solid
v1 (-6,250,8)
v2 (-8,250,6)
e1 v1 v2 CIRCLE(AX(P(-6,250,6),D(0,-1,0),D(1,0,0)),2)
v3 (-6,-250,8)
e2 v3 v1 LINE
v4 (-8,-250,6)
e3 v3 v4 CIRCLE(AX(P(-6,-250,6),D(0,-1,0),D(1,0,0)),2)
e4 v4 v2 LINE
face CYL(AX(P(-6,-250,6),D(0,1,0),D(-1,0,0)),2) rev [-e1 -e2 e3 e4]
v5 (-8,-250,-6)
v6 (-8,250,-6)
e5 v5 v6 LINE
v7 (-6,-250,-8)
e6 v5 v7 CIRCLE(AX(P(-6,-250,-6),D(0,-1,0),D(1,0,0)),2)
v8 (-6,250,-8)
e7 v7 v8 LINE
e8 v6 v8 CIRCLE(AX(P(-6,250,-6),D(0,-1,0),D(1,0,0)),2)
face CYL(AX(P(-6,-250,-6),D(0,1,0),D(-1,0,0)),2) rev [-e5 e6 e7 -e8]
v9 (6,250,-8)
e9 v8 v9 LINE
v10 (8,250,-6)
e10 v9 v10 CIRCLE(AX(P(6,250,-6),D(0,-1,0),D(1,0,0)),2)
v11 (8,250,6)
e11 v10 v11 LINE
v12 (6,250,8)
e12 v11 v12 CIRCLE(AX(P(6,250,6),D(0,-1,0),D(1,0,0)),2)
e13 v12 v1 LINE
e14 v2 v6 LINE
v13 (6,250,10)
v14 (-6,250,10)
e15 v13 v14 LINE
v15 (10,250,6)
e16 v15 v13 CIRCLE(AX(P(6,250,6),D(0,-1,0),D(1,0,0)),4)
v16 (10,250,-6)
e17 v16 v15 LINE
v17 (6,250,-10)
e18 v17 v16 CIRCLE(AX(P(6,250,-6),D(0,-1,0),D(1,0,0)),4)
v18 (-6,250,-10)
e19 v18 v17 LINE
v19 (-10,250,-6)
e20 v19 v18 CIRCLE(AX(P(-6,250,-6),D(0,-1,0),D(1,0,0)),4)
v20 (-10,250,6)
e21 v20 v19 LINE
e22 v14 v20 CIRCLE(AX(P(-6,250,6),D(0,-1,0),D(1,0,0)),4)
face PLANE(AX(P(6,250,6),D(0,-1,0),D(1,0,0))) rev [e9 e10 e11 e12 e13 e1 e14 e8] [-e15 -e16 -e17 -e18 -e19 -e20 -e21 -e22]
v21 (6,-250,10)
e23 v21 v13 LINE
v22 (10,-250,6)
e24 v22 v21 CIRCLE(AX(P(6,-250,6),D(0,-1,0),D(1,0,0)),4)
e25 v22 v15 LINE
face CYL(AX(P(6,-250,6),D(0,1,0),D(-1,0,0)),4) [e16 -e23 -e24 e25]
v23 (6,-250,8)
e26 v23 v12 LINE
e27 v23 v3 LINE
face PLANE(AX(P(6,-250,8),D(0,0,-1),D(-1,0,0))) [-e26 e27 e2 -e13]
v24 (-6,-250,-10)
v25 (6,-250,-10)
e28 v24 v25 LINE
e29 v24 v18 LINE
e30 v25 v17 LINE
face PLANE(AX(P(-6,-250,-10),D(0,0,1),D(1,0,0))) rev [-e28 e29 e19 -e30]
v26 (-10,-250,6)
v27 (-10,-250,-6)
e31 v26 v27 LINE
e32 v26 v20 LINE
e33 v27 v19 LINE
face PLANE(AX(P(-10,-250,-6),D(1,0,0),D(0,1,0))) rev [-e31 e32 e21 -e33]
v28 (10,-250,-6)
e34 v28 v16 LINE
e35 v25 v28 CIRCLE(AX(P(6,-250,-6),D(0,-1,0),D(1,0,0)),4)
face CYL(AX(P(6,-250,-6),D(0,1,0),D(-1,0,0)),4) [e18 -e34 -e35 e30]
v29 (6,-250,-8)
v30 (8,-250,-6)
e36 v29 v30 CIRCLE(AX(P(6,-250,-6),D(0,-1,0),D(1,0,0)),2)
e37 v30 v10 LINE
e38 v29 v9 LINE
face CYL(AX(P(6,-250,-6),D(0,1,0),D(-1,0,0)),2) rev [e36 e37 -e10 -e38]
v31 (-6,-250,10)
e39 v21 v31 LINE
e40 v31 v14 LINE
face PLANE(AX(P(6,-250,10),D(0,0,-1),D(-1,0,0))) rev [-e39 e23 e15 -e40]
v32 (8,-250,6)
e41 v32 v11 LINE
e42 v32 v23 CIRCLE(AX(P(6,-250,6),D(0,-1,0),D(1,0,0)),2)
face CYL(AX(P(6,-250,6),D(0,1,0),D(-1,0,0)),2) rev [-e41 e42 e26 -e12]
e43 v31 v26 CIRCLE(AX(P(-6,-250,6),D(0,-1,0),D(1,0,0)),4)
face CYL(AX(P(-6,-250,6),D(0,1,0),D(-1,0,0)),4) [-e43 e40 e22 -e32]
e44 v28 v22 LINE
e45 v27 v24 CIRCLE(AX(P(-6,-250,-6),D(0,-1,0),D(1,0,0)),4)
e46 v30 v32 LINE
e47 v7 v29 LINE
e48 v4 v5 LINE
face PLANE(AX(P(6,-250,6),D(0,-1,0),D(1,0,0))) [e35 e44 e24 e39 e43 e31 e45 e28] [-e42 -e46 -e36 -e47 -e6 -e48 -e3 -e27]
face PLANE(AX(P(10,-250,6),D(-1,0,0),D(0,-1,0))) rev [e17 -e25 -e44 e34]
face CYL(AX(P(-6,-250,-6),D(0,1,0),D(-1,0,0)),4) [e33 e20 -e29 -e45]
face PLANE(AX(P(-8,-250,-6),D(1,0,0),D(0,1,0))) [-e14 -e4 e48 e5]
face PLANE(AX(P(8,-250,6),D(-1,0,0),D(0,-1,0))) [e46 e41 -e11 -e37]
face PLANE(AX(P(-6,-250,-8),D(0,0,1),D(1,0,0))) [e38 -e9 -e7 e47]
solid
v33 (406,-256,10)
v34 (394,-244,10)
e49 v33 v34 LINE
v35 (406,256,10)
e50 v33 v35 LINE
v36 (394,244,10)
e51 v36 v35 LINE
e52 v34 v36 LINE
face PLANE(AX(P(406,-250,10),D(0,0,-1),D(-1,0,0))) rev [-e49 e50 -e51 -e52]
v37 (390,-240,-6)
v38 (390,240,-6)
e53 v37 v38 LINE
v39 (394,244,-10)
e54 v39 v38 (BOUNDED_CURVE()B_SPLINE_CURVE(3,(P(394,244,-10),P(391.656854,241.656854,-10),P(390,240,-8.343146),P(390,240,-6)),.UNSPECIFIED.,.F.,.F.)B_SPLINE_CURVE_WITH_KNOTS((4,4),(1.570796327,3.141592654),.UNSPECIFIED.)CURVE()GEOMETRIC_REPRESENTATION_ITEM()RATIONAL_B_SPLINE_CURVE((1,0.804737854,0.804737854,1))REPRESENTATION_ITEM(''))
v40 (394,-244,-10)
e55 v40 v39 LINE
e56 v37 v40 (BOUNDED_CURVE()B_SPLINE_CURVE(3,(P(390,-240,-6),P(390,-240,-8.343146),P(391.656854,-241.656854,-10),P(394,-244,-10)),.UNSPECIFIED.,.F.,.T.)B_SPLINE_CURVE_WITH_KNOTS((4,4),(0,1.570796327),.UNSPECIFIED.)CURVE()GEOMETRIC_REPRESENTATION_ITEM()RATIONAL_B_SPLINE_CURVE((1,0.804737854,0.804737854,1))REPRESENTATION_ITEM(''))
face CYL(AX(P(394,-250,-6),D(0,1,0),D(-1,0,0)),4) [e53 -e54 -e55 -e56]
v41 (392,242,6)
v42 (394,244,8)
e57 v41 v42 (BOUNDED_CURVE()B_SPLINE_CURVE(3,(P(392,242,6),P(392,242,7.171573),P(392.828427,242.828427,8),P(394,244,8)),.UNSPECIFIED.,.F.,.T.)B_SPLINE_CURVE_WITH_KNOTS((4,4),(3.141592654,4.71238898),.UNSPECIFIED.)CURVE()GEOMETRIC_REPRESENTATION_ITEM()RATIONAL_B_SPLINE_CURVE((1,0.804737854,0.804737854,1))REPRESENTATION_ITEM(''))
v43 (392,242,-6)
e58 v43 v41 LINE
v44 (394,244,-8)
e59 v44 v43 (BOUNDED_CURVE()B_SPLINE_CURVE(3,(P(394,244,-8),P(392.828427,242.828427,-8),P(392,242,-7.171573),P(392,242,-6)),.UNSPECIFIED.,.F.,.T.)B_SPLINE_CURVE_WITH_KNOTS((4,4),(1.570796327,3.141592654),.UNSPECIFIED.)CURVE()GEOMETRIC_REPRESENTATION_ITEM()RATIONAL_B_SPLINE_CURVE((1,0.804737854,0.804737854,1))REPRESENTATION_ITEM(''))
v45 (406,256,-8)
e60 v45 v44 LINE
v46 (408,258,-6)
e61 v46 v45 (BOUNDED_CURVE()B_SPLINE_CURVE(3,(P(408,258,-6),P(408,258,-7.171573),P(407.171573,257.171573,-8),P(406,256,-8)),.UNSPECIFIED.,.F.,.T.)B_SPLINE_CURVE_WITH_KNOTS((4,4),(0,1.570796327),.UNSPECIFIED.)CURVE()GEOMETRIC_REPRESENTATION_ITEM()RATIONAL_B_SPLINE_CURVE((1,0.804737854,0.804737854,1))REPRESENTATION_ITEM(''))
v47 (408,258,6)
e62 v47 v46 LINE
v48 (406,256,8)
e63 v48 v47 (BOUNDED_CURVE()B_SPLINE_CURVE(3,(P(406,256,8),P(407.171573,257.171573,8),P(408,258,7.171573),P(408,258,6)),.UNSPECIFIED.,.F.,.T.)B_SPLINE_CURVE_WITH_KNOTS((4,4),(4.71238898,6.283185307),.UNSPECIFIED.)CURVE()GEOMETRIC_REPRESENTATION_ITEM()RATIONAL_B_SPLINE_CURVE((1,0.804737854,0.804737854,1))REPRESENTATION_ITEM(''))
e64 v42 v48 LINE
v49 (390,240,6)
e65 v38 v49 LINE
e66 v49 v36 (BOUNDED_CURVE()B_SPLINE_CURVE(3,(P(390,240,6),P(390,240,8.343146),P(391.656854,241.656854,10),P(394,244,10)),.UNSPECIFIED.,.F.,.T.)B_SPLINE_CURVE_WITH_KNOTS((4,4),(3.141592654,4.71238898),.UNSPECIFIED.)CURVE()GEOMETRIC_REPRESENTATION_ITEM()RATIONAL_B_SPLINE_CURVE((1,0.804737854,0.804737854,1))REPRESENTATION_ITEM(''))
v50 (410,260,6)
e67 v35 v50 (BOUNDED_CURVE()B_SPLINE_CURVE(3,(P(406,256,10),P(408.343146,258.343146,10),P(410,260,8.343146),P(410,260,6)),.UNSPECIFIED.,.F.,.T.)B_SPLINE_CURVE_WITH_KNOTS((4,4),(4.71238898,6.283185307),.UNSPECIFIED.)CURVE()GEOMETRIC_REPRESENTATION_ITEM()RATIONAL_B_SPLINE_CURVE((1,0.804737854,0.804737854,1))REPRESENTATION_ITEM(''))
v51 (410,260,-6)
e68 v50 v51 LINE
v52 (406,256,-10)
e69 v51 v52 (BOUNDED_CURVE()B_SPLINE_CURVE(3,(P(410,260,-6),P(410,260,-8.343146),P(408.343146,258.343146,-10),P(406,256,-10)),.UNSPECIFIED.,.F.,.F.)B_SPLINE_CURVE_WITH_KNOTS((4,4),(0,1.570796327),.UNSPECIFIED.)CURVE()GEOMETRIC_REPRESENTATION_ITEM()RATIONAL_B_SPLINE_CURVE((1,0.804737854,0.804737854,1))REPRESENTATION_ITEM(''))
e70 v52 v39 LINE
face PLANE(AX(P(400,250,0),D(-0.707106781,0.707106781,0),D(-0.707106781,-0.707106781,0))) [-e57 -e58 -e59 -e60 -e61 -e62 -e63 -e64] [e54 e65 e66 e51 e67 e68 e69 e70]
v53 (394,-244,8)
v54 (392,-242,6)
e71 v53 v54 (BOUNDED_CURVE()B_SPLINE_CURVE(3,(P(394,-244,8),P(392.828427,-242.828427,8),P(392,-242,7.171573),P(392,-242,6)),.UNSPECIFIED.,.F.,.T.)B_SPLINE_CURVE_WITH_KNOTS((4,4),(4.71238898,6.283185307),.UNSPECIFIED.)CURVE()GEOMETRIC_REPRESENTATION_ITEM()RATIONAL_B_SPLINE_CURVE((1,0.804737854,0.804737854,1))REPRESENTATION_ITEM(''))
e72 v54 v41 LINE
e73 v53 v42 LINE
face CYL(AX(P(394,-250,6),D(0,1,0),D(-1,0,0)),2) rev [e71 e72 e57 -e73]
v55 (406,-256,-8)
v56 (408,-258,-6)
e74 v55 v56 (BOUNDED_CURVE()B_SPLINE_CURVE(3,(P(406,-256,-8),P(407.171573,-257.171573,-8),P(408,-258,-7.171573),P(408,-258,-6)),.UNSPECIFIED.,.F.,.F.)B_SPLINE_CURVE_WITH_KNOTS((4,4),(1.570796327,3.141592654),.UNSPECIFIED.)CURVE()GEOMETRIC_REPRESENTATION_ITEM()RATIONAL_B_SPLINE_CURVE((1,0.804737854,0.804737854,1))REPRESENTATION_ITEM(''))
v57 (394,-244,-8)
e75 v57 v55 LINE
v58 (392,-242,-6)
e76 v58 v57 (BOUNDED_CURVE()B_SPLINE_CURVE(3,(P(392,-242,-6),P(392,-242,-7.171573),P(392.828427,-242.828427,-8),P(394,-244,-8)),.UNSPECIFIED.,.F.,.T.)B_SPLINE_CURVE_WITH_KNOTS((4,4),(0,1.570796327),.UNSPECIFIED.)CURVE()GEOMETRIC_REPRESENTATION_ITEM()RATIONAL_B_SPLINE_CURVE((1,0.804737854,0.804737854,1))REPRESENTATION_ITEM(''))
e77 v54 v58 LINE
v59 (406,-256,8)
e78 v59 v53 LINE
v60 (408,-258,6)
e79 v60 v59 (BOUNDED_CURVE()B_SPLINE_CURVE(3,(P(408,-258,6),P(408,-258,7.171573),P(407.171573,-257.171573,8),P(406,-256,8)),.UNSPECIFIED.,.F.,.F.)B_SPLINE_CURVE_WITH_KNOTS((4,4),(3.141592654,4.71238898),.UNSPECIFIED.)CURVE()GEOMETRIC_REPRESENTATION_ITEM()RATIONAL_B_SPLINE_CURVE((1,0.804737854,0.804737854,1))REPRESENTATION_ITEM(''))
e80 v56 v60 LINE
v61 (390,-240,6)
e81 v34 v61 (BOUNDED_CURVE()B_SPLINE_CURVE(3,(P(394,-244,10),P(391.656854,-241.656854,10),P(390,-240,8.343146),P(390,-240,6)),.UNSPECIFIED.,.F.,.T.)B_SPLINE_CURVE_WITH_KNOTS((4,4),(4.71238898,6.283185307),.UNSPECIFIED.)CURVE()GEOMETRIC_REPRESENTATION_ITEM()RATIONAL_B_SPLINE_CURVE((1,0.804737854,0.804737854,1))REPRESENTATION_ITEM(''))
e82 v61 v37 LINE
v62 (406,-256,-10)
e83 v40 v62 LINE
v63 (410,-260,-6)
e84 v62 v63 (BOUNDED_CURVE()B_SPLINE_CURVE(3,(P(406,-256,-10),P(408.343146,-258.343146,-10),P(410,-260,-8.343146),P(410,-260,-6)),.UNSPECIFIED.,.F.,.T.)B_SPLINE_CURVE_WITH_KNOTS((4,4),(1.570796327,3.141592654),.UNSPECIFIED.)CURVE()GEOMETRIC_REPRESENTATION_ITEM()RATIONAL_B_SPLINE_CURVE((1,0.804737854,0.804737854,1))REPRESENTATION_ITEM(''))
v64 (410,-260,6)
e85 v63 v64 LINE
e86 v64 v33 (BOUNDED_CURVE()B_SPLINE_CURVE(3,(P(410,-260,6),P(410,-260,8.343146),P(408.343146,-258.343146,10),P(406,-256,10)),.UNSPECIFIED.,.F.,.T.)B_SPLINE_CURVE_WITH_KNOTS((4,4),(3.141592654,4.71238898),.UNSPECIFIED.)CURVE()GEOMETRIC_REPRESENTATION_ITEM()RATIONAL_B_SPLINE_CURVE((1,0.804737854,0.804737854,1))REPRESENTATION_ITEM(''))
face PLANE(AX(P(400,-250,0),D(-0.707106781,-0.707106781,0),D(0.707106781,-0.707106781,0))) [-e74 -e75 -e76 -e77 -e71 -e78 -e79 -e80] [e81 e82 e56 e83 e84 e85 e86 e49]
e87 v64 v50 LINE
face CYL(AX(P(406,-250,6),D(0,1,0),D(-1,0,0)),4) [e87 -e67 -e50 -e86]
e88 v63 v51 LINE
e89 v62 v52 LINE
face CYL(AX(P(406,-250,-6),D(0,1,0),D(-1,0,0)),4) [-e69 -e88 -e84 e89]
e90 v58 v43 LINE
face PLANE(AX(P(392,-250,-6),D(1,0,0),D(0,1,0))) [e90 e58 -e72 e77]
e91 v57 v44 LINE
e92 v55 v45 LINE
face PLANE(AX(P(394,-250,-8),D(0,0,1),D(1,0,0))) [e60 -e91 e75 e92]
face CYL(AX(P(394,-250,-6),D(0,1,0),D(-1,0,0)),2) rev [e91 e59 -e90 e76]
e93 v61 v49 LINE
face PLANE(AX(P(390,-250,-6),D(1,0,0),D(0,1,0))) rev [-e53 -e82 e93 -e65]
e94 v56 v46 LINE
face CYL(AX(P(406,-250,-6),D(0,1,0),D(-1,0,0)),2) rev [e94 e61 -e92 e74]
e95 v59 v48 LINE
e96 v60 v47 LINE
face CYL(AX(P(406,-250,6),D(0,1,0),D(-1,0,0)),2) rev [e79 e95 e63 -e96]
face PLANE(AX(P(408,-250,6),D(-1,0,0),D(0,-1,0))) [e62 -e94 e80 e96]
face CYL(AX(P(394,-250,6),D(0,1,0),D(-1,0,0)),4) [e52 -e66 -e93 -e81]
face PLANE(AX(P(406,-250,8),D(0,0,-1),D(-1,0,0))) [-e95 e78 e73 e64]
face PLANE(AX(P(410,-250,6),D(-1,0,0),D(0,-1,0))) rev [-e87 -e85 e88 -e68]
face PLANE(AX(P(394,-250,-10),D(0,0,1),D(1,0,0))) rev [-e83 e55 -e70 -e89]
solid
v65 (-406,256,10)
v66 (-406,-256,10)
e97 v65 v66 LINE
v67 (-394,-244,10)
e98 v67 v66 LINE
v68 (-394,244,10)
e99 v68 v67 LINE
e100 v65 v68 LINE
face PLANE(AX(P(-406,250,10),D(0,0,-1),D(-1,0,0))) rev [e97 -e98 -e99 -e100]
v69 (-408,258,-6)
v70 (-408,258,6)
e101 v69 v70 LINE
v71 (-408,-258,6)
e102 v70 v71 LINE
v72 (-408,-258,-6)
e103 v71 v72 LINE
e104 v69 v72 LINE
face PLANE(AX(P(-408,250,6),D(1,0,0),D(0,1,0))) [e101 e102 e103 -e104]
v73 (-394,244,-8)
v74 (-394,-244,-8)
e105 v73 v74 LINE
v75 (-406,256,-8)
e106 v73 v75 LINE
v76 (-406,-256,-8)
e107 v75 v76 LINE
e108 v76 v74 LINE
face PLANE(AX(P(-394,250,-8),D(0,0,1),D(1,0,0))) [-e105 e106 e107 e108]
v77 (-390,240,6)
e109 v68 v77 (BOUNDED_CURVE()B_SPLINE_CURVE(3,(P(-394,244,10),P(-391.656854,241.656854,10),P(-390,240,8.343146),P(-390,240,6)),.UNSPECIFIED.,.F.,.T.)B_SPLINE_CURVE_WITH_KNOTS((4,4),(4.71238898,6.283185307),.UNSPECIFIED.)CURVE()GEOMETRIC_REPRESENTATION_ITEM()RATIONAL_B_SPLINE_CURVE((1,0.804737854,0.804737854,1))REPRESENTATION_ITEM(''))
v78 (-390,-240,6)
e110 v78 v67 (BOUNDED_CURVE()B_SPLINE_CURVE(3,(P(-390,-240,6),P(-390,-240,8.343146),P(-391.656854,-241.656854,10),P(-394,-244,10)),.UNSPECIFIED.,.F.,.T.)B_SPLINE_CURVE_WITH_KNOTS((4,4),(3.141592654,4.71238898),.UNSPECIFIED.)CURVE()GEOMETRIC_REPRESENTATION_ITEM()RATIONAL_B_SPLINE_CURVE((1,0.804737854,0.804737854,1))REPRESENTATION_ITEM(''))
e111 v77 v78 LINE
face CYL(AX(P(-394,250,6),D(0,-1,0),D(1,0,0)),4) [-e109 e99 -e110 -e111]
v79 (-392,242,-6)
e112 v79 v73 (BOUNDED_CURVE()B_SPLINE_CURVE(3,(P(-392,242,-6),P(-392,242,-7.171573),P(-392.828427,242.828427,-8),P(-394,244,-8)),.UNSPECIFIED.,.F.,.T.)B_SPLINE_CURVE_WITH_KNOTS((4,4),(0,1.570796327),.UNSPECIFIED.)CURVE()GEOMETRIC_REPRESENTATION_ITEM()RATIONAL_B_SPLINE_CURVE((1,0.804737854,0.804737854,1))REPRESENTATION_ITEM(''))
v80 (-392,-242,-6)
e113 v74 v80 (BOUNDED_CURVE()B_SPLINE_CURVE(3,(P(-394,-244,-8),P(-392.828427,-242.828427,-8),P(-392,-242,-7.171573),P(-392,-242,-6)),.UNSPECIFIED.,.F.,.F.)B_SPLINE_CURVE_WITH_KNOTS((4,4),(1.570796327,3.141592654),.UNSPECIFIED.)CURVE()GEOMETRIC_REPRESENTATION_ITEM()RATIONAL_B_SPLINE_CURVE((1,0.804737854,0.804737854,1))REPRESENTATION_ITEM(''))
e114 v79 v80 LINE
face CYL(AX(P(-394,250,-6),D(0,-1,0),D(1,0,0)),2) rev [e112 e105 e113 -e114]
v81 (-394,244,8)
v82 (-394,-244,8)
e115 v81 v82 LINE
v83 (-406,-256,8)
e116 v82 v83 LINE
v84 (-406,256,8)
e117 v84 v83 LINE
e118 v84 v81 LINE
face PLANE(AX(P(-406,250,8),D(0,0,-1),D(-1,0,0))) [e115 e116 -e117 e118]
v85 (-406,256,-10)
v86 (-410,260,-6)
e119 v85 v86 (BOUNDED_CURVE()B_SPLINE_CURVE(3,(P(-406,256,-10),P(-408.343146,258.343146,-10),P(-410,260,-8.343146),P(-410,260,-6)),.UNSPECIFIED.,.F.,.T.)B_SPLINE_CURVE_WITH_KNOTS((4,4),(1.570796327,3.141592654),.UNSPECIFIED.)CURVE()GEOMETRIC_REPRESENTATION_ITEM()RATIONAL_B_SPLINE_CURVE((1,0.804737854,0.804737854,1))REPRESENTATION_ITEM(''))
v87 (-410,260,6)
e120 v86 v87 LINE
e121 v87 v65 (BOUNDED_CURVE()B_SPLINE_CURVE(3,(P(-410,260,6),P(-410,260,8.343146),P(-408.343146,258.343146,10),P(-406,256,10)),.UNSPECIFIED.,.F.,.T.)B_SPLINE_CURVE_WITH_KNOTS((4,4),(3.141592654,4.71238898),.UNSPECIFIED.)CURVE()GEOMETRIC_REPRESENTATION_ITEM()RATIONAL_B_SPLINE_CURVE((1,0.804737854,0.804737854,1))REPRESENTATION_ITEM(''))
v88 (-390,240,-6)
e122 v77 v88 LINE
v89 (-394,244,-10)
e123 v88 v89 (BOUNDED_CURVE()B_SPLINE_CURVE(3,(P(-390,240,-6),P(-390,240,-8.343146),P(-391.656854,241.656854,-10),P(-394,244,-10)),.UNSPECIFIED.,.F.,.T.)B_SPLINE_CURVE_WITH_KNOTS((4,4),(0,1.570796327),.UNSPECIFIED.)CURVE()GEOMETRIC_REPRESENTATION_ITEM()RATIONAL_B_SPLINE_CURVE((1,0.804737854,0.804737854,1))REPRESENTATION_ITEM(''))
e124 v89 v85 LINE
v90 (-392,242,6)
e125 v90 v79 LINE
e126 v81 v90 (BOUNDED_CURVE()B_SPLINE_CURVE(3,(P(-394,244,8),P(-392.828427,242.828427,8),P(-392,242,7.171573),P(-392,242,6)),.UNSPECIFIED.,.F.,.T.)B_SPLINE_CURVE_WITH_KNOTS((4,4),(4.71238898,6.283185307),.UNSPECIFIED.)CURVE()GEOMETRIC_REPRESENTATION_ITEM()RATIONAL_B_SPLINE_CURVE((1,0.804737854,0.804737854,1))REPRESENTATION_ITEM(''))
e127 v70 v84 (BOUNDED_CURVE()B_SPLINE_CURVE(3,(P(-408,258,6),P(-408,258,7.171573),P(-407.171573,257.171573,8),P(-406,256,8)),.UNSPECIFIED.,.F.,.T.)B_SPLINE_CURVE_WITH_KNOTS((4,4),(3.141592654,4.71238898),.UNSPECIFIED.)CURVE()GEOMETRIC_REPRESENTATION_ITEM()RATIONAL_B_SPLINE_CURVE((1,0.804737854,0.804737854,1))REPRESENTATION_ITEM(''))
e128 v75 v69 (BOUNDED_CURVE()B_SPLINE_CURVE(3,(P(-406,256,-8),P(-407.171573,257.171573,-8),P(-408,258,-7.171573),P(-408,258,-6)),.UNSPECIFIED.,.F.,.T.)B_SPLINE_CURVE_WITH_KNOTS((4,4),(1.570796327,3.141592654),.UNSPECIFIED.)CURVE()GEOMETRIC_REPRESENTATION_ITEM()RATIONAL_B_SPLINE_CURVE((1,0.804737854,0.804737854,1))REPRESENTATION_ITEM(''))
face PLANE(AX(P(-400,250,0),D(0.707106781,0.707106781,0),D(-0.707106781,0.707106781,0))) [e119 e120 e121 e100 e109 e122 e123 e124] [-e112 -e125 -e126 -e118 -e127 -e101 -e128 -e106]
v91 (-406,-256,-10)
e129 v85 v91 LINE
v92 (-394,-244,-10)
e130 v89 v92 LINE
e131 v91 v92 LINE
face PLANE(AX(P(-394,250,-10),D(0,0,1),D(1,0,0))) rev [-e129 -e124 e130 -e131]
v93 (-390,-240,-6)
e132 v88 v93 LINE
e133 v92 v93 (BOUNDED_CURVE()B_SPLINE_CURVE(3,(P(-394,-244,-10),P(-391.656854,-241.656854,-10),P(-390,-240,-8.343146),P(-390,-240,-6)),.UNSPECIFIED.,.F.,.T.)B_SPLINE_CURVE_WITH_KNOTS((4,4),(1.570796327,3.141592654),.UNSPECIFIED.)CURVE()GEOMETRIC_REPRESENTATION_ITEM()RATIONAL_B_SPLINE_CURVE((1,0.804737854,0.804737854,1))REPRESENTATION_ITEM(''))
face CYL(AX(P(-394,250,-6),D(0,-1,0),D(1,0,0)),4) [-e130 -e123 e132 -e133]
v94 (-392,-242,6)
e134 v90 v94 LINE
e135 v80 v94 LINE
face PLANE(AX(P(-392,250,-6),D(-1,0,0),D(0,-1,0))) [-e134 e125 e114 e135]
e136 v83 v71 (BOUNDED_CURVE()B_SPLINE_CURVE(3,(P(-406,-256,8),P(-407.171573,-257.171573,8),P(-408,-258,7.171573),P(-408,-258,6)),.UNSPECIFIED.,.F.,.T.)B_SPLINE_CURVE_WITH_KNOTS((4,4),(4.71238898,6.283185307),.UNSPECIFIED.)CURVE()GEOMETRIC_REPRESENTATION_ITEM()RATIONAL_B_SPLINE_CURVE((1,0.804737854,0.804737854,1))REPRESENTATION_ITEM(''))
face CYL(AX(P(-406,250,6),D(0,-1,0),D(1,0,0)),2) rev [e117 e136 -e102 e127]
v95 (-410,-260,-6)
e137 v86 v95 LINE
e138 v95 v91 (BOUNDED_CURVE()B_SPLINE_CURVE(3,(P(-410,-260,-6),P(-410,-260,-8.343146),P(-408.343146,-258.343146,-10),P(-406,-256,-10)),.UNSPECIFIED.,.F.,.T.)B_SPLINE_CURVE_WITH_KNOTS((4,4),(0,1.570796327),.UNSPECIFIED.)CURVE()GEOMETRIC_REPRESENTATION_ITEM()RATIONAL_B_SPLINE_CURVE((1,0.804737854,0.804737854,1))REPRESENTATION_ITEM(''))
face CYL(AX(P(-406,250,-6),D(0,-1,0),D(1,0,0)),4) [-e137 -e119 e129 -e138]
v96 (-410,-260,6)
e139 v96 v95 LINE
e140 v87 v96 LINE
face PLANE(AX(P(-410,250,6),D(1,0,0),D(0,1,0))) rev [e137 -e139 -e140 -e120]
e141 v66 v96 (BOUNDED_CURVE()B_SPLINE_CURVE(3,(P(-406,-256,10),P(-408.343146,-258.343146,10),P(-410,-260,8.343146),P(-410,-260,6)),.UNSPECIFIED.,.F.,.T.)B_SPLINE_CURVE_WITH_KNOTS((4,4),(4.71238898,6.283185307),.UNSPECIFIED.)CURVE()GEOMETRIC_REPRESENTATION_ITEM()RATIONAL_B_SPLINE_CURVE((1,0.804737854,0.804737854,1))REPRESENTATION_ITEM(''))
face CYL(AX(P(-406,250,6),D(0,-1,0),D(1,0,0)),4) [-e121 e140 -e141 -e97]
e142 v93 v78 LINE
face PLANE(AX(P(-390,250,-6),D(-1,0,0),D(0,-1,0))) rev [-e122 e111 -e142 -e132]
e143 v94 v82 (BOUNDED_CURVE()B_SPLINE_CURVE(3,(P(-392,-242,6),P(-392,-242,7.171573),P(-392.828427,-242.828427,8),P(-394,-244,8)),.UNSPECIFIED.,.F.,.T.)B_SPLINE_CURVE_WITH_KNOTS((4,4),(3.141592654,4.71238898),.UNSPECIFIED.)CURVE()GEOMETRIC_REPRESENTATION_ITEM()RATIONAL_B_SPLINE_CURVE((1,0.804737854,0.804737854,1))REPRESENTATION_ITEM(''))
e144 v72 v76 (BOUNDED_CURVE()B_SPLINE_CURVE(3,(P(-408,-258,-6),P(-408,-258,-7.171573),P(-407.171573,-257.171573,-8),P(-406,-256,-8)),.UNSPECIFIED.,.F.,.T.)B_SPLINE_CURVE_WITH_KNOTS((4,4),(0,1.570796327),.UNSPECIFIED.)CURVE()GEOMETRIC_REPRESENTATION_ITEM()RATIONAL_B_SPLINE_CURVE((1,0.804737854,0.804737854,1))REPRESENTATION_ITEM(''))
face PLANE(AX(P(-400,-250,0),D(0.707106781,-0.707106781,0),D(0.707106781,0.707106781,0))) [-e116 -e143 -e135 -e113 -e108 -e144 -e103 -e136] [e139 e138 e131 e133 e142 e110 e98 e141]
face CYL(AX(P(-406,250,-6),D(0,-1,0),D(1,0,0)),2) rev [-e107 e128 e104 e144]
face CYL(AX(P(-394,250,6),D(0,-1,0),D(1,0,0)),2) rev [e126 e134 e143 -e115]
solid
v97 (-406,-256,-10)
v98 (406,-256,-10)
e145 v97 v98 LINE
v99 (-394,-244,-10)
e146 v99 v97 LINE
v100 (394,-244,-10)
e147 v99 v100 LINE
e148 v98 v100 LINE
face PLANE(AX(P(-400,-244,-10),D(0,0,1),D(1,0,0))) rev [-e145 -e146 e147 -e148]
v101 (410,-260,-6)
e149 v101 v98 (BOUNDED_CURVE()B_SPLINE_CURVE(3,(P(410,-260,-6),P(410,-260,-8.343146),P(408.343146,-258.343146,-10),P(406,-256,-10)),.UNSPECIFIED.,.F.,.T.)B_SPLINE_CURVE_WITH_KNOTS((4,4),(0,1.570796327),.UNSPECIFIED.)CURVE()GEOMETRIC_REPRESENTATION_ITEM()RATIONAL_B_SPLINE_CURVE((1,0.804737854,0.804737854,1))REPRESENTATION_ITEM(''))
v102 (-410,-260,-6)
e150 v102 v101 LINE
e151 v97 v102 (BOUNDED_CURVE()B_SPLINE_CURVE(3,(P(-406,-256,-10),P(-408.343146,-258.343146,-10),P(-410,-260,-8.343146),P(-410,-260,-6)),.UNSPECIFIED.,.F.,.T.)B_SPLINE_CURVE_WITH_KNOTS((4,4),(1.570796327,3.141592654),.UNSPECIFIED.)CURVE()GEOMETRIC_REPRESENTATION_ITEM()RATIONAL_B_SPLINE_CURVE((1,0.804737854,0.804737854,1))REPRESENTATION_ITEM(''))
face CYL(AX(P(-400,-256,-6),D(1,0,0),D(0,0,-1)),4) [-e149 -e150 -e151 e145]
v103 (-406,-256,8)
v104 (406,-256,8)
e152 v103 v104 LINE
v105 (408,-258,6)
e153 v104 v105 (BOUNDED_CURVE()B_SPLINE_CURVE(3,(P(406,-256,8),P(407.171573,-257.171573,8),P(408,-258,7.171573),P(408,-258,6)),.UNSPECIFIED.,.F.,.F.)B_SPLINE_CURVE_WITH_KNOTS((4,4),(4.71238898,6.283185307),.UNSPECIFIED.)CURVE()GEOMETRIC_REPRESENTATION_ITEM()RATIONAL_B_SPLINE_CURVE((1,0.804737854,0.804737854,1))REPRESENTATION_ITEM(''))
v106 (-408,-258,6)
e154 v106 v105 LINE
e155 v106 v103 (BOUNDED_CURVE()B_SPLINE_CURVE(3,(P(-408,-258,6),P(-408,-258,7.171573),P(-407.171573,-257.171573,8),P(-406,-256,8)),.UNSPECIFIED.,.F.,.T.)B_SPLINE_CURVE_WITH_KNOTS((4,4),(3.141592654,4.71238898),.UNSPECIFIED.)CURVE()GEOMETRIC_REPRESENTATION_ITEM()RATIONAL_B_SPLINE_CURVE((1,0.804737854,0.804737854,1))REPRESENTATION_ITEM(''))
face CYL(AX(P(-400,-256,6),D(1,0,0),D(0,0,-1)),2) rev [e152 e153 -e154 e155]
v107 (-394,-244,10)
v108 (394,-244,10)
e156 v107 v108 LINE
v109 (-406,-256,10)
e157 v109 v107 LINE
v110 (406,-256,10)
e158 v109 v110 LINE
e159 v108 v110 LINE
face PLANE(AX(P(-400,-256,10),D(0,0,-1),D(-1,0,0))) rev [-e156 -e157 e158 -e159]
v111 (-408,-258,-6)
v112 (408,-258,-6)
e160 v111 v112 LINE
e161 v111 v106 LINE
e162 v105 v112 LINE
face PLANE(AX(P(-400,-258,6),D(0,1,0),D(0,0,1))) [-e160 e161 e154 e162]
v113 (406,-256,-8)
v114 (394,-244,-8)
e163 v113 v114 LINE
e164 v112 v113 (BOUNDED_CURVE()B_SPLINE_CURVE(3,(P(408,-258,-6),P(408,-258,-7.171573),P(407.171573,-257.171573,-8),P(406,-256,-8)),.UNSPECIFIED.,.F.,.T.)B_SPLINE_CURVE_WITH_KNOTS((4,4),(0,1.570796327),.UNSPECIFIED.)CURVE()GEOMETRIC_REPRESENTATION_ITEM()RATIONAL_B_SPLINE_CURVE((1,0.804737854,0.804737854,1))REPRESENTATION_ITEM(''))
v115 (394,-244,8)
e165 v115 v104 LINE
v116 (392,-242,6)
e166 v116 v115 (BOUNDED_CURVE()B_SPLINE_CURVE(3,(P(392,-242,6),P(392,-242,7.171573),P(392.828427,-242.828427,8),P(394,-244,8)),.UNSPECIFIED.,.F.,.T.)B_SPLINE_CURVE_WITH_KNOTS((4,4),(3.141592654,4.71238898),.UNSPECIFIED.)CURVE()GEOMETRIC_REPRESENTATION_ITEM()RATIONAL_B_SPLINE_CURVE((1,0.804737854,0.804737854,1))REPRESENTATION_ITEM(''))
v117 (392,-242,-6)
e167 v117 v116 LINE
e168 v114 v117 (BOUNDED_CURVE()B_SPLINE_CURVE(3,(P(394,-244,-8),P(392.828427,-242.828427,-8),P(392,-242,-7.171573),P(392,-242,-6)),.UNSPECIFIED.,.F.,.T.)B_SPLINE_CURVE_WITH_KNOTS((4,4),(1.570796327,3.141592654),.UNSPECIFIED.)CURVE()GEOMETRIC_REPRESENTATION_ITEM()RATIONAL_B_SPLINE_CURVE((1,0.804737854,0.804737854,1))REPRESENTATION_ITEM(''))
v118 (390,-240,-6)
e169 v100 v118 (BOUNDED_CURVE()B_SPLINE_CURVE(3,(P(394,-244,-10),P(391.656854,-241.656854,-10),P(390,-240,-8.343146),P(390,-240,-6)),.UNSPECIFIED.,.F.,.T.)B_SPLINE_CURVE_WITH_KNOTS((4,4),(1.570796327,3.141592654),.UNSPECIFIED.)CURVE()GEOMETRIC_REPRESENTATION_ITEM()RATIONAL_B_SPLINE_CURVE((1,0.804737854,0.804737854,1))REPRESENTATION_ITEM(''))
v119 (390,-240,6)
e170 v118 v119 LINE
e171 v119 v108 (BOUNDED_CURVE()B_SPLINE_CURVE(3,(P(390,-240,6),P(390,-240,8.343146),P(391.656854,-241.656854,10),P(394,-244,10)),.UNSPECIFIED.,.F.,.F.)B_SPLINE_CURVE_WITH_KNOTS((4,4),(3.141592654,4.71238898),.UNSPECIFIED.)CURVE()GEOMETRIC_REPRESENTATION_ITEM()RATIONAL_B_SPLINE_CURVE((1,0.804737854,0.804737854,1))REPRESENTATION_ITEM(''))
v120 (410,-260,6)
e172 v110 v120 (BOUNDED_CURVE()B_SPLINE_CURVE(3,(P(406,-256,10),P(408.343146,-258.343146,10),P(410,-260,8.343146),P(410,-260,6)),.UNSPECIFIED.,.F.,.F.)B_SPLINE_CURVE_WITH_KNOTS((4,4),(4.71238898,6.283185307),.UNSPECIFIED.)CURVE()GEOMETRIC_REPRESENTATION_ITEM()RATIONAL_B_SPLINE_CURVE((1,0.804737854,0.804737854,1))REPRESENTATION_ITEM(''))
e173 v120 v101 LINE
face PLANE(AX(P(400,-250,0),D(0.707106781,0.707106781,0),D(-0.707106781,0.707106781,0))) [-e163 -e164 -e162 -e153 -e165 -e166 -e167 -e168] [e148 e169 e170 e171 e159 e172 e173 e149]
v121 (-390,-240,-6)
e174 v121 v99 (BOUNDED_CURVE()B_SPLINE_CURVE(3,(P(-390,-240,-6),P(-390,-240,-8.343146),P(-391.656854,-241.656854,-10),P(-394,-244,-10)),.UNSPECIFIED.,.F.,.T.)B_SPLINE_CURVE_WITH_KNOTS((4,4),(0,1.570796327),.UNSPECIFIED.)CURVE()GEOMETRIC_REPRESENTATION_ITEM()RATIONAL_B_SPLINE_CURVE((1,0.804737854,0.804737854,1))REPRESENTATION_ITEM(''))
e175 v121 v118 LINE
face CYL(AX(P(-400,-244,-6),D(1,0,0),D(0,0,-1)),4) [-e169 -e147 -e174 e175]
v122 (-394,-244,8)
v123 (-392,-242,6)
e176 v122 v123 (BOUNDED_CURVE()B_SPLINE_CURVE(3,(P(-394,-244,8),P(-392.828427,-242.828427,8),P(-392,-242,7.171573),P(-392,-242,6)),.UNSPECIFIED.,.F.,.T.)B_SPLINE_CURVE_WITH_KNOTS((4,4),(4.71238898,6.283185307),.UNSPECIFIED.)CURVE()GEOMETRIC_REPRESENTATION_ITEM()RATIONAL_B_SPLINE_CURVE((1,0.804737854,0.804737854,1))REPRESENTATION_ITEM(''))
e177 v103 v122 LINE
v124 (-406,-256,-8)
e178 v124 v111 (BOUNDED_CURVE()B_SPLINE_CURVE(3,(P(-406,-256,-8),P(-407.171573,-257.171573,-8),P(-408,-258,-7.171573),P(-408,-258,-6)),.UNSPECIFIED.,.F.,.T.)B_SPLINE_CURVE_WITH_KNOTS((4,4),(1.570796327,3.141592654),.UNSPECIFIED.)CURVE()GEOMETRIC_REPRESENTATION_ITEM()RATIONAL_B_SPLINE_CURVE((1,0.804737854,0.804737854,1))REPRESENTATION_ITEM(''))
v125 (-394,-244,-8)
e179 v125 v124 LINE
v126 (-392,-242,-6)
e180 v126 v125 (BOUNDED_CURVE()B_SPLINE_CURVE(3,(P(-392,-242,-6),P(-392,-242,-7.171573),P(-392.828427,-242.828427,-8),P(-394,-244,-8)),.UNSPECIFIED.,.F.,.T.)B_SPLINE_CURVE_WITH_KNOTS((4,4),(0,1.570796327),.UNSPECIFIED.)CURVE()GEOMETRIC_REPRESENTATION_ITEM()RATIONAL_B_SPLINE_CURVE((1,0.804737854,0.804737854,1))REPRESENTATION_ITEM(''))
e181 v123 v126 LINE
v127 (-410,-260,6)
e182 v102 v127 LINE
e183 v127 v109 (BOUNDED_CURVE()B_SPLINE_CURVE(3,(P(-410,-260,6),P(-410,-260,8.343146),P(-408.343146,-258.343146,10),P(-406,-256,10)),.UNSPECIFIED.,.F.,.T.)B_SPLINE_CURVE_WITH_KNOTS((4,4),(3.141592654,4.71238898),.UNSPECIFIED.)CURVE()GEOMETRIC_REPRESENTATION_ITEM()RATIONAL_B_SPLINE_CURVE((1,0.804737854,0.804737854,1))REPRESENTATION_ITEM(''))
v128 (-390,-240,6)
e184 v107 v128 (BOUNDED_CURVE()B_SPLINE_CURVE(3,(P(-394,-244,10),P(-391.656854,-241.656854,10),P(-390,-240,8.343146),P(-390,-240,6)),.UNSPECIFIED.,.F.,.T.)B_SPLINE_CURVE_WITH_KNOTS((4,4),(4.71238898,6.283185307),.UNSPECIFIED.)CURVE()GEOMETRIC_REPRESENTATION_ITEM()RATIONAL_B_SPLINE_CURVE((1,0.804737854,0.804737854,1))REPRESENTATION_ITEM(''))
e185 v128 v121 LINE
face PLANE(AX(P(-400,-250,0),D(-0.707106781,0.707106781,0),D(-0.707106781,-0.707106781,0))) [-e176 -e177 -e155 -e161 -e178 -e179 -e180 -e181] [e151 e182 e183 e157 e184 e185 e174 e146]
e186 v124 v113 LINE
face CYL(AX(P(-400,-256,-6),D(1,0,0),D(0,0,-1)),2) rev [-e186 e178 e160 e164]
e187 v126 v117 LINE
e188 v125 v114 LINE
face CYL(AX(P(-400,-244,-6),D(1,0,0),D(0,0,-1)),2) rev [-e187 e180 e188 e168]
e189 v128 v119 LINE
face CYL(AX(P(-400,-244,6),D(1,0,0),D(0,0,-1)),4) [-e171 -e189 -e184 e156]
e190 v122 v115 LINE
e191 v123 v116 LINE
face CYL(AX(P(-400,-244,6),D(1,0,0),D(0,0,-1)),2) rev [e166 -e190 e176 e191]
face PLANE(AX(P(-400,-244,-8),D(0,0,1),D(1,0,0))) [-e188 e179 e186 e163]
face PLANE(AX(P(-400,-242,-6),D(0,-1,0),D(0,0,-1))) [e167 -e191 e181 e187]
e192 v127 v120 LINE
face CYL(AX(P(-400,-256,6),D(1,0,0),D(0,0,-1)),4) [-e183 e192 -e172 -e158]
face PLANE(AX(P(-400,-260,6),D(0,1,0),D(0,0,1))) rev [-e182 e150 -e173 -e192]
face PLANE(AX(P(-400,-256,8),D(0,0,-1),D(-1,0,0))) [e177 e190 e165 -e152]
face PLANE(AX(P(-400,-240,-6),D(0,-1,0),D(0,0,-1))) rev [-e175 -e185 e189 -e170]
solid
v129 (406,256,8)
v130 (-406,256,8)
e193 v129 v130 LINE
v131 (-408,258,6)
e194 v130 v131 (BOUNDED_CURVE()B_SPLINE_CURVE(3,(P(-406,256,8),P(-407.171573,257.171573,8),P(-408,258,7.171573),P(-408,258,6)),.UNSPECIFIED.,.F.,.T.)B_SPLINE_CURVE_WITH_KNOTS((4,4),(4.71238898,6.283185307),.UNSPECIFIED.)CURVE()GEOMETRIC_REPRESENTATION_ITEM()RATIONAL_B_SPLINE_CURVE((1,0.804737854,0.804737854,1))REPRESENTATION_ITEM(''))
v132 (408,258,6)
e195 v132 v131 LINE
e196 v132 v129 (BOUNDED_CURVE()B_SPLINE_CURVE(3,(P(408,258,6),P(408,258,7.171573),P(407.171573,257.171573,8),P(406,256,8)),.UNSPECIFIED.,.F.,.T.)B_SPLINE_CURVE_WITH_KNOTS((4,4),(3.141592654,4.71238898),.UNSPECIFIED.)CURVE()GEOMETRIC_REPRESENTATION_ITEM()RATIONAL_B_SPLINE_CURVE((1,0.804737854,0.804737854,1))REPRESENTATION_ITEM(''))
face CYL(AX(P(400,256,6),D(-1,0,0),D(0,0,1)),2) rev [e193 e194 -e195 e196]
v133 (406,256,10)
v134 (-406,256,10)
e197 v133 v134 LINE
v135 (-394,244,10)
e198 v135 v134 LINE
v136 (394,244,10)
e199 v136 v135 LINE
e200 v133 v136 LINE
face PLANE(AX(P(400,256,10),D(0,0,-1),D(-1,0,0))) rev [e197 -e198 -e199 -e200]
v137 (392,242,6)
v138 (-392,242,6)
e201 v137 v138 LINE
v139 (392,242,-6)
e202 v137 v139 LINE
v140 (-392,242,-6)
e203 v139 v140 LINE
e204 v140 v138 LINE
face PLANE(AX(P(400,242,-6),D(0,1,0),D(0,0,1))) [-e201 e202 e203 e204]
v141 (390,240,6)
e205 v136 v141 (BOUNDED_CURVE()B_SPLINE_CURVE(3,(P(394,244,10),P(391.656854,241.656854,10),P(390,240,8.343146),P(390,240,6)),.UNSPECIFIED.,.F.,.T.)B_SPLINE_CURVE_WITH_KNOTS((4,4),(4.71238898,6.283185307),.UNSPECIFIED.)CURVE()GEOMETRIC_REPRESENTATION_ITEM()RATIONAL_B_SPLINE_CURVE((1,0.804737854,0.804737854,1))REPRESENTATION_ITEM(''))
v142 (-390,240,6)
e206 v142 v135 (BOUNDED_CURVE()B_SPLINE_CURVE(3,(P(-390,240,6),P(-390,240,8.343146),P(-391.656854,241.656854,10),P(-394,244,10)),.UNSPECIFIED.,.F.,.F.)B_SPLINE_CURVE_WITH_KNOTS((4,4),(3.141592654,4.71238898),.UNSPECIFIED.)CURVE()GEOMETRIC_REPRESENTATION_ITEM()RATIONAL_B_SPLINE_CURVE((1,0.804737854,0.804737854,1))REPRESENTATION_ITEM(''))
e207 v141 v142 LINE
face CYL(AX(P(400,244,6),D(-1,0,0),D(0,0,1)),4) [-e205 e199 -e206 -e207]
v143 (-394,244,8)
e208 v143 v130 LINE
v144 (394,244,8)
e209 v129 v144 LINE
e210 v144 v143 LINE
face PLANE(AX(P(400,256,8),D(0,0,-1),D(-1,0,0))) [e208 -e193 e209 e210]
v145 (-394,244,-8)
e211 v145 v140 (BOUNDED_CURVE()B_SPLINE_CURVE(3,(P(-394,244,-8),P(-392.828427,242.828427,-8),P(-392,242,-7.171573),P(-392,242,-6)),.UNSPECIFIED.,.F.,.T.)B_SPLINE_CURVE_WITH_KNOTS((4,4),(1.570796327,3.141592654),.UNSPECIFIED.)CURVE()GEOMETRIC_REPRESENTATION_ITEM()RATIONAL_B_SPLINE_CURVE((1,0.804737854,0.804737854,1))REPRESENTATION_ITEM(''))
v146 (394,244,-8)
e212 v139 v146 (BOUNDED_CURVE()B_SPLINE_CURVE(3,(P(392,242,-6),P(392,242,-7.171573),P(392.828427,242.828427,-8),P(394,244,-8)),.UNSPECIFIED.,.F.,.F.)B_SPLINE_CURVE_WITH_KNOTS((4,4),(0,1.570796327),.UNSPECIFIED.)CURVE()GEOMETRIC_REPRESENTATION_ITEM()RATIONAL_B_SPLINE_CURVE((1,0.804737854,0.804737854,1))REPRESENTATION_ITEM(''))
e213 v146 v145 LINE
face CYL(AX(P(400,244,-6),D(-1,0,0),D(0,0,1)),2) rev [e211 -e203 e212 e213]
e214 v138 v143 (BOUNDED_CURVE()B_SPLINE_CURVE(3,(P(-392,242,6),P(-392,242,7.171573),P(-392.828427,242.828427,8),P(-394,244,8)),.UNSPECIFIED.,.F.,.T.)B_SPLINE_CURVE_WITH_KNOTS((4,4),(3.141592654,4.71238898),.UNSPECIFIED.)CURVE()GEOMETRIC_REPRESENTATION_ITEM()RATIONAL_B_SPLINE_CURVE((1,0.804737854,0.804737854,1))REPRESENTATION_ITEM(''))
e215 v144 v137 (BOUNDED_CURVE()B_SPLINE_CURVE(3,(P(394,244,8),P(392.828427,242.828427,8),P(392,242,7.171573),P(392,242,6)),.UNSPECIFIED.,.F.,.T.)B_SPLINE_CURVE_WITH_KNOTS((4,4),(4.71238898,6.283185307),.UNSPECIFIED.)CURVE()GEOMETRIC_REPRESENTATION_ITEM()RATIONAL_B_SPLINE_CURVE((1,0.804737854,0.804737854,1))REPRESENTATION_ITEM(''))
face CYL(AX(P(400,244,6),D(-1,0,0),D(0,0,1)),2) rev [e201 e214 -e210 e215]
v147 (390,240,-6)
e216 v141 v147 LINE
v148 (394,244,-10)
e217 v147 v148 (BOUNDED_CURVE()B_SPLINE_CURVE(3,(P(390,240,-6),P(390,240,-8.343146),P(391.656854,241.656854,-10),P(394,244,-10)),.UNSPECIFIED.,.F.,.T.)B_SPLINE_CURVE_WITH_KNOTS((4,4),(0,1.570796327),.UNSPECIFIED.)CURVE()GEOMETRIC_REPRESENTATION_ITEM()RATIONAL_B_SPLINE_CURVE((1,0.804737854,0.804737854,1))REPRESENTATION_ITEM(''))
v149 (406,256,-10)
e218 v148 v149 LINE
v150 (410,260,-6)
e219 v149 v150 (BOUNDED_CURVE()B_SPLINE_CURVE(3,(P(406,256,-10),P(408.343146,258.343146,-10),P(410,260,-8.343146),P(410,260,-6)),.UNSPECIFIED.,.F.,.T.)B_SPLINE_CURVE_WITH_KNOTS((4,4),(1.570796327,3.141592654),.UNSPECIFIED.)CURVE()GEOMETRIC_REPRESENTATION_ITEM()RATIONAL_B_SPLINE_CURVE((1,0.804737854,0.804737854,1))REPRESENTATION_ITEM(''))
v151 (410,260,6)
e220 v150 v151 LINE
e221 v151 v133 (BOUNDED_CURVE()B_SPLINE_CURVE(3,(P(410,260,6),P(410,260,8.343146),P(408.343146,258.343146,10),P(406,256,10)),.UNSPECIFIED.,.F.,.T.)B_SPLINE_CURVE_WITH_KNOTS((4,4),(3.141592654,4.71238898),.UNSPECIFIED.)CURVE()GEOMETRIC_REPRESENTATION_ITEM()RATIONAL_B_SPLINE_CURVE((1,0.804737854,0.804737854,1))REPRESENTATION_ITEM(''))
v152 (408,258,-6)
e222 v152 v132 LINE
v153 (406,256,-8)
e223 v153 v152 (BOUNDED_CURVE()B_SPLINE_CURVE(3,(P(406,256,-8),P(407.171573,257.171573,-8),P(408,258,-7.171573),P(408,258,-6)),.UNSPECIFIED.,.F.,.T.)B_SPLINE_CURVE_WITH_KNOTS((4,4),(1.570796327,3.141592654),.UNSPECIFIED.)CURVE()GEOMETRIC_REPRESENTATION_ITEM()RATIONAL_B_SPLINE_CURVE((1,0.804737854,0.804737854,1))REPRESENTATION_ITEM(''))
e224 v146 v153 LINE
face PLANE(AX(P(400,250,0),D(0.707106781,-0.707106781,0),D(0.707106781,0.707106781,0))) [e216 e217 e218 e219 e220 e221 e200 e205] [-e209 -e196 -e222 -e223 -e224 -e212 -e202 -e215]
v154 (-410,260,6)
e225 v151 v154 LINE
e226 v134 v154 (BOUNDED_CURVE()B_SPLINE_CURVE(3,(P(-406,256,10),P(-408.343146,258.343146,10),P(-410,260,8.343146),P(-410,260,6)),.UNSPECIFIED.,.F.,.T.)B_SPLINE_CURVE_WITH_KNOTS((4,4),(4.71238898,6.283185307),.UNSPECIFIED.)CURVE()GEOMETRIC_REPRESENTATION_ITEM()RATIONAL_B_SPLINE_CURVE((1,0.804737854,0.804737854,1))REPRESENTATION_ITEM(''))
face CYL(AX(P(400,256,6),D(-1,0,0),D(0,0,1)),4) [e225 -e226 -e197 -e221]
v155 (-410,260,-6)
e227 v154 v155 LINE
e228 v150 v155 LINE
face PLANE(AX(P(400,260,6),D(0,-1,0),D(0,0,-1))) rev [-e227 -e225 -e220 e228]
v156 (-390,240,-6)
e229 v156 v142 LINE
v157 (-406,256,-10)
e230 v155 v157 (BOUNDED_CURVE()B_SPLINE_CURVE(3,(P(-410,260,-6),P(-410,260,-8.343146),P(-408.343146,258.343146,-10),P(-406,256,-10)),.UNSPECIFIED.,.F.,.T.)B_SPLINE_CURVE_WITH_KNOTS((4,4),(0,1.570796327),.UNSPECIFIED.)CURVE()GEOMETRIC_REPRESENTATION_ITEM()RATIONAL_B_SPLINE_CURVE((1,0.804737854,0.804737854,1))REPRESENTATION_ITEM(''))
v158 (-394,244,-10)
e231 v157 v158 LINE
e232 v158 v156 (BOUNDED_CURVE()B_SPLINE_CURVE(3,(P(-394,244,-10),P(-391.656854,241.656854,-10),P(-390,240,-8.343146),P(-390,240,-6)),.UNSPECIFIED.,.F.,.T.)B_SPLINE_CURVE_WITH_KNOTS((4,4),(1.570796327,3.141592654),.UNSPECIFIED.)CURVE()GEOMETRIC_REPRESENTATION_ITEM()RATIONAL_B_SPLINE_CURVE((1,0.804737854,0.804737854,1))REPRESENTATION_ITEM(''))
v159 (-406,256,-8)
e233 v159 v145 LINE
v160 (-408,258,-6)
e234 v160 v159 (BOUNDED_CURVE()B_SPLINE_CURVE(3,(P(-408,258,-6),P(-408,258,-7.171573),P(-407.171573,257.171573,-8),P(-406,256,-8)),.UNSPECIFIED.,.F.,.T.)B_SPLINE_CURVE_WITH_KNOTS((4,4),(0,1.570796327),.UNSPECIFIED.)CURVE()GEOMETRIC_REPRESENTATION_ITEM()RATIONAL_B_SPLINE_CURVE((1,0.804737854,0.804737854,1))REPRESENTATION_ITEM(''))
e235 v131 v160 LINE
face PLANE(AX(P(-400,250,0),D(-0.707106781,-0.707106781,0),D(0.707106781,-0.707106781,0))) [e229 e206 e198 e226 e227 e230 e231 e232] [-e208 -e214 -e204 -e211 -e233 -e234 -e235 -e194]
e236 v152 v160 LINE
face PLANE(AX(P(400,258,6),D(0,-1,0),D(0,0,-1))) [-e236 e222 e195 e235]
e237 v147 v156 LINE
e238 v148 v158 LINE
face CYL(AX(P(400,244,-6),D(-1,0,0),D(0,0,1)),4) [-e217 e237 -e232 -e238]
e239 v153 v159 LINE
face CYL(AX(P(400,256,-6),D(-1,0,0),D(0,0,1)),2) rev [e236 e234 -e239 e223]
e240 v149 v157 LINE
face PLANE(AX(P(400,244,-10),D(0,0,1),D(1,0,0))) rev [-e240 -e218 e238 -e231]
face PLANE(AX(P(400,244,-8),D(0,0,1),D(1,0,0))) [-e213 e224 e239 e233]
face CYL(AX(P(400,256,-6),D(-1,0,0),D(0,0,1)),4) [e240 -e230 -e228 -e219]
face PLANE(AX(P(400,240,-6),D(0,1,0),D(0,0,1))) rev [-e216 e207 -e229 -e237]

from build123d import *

# Parameters (mm, degrees)
SQUARE_TUBE_20_X_20_X_2_1_DEPTH      = 815.142135624
SQUARE_TUBE_20_X_20_X_2_1_DEPTH_BACK = 15.142135624
SQUARE_TUBE_20_X_20_X_2_1_2_DEPTH    = 530.284271247
SQUARE_TUBE_20_X_20_X_2_1_3_DEPTH    = 830.284271247
SQUARE_TUBE_20_X_20_X_2_1_4_DEPTH    = 530.284271247
SQUARE_TUBE_20_X_20_X_2_2_DEPTH      = 500


with BuildPart() as part:
    # Sketch1 → Square tube 20 X 20 X 2(1) (new, two sides: drawn at the far end of the back side and taken through both)
    with BuildSketch(Plane(origin=(-400, 250, 0), x_dir=(0, 1, 0), z_dir=(1, 0, 0)).offset(-SQUARE_TUBE_20_X_20_X_2_1_DEPTH_BACK)):
        with BuildLine():
            Line((-6, -10), (6, -10))
            ThreePointArc((6, -10), (8.828427125, -8.828427125), (10, -6))
            Line((10, -6), (10, 6))
            ThreePointArc((10, 6), (8.828427125, 8.828427125), (6, 10))
            Line((6, 10), (-6, 10))
            ThreePointArc((-6, 10), (-8.828427125, 8.828427125), (-10, 6))
            Line((-10, 6), (-10, -6))
            ThreePointArc((-10, -6), (-8.828427125, -8.828427125), (-6, -10))
        make_face()
        with BuildLine():
            Line((-6, -8), (6, -8))
            ThreePointArc((6, -8), (7.414213562, -7.414213562), (8, -6))
            Line((8, -6), (8, 6))
            ThreePointArc((8, 6), (7.414213562, 7.414213562), (6, 8))
            Line((6, 8), (-6, 8))
            ThreePointArc((-6, 8), (-7.414213562, 7.414213562), (-8, 6))
            Line((-8, 6), (-8, -6))
            ThreePointArc((-8, -6), (-7.414213562, -7.414213562), (-6, -8))
        make_face(mode=Mode.SUBTRACT)
    extrude(amount=SQUARE_TUBE_20_X_20_X_2_1_DEPTH + SQUARE_TUBE_20_X_20_X_2_1_DEPTH_BACK)

    # Square tube 20 X 20 X 2(1) mitre 1
    split(bisect_by=Plane(origin=(-400, 250, 0), x_dir=(-0.707106781, 0.707106781, 0), z_dir=(0.707106781, 0.707106781, 0)), keep=Keep.TOP)

    # Square tube 20 X 20 X 2(1) mitre 2
    split(bisect_by=Plane(origin=(400, 250, 0), x_dir=(-0.707106781, -0.707106781, 0), z_dir=(-0.707106781, 0.707106781, 0)), keep=Keep.TOP)


with BuildPart() as body_2:
    # Sketch1 on segment 2 (carried to segment 2) → Square tube 20 X 20 X 2_1 2 (new body)
    with BuildSketch(Plane(origin=(400, 265.142135624, 0), x_dir=(1, 0, 0), z_dir=(0, -1, 0))):
        with BuildLine():
            Line((-6, -10), (6, -10))
            ThreePointArc((6, -10), (8.828427125, -8.828427125), (10, -6))
            Line((10, -6), (10, 6))
            ThreePointArc((10, 6), (8.828427125, 8.828427125), (6, 10))
            Line((6, 10), (-6, 10))
            ThreePointArc((-6, 10), (-8.828427125, 8.828427125), (-10, 6))
            Line((-10, 6), (-10, -6))
            ThreePointArc((-10, -6), (-8.828427125, -8.828427125), (-6, -10))
        make_face()
        with BuildLine():
            Line((-6, -8), (6, -8))
            ThreePointArc((6, -8), (7.414213562, -7.414213562), (8, -6))
            Line((8, -6), (8, 6))
            ThreePointArc((8, 6), (7.414213562, 7.414213562), (6, 8))
            Line((6, 8), (-6, 8))
            ThreePointArc((-6, 8), (-7.414213562, 7.414213562), (-8, 6))
            Line((-8, 6), (-8, -6))
            ThreePointArc((-8, -6), (-7.414213562, -7.414213562), (-6, -8))
        make_face(mode=Mode.SUBTRACT)
    extrude(amount=SQUARE_TUBE_20_X_20_X_2_1_2_DEPTH)

    # Square tube 20 X 20 X 2_1 2 mitre 1
    split(bisect_by=Plane(origin=(400, 250, 0), x_dir=(0.707106781, 0.707106781, 0), z_dir=(0.707106781, -0.707106781, 0)), keep=Keep.TOP)

    # Square tube 20 X 20 X 2_1 2 mitre 2
    split(bisect_by=Plane(origin=(400, -250, 0), x_dir=(-0.707106781, 0.707106781, 0), z_dir=(0.707106781, 0.707106781, 0)), keep=Keep.TOP)


with BuildPart() as body_3:
    # Sketch1 on segment 3 (carried to segment 3) → Square tube 20 X 20 X 2_1 3 (new body)
    with BuildSketch(Plane(origin=(415.142135624, -250, 0), x_dir=(0, -1, 0), z_dir=(-1, 0, 0))):
        with BuildLine():
            Line((-6, -10), (6, -10))
            ThreePointArc((6, -10), (8.828427125, -8.828427125), (10, -6))
            Line((10, -6), (10, 6))
            ThreePointArc((10, 6), (8.828427125, 8.828427125), (6, 10))
            Line((6, 10), (-6, 10))
            ThreePointArc((-6, 10), (-8.828427125, 8.828427125), (-10, 6))
            Line((-10, 6), (-10, -6))
            ThreePointArc((-10, -6), (-8.828427125, -8.828427125), (-6, -10))
        make_face()
        with BuildLine():
            Line((-6, -8), (6, -8))
            ThreePointArc((6, -8), (7.414213562, -7.414213562), (8, -6))
            Line((8, -6), (8, 6))
            ThreePointArc((8, 6), (7.414213562, 7.414213562), (6, 8))
            Line((6, 8), (-6, 8))
            ThreePointArc((-6, 8), (-7.414213562, 7.414213562), (-8, 6))
            Line((-8, 6), (-8, -6))
            ThreePointArc((-8, -6), (-7.414213562, -7.414213562), (-6, -8))
        make_face(mode=Mode.SUBTRACT)
    extrude(amount=SQUARE_TUBE_20_X_20_X_2_1_3_DEPTH)

    # Square tube 20 X 20 X 2_1 3 mitre 1
    split(bisect_by=Plane(origin=(-400, -250, 0), x_dir=(0.707106781, 0.707106781, 0), z_dir=(0.707106781, -0.707106781, 0)), keep=Keep.TOP)

    # Square tube 20 X 20 X 2_1 3 mitre 2
    split(bisect_by=Plane(origin=(400, -250, 0), x_dir=(0.707106781, -0.707106781, 0), z_dir=(-0.707106781, -0.707106781, 0)), keep=Keep.TOP)


with BuildPart() as body_4:
    # Sketch1 on segment 4 (carried to segment 4) → Square tube 20 X 20 X 2_1 4 (new body)
    with BuildSketch(Plane(origin=(-400, -265.142135624, 0), x_dir=(-1, 0, 0), z_dir=(0, 1, 0))):
        with BuildLine():
            Line((-6, -10), (6, -10))
            ThreePointArc((6, -10), (8.828427125, -8.828427125), (10, -6))
            Line((10, -6), (10, 6))
            ThreePointArc((10, 6), (8.828427125, 8.828427125), (6, 10))
            Line((6, 10), (-6, 10))
            ThreePointArc((-6, 10), (-8.828427125, 8.828427125), (-10, 6))
            Line((-10, 6), (-10, -6))
            ThreePointArc((-10, -6), (-8.828427125, -8.828427125), (-6, -10))
        make_face()
        with BuildLine():
            Line((-6, -8), (6, -8))
            ThreePointArc((6, -8), (7.414213562, -7.414213562), (8, -6))
            Line((8, -6), (8, 6))
            ThreePointArc((8, 6), (7.414213562, 7.414213562), (6, 8))
            Line((6, 8), (-6, 8))
            ThreePointArc((-6, 8), (-7.414213562, 7.414213562), (-8, 6))
            Line((-8, 6), (-8, -6))
            ThreePointArc((-8, -6), (-7.414213562, -7.414213562), (-6, -8))
        make_face(mode=Mode.SUBTRACT)
    extrude(amount=SQUARE_TUBE_20_X_20_X_2_1_4_DEPTH)

    # Square tube 20 X 20 X 2_1 4 mitre 1
    split(bisect_by=Plane(origin=(-400, 250, 0), x_dir=(0.707106781, -0.707106781, 0), z_dir=(-0.707106781, -0.707106781, 0)), keep=Keep.TOP)

    # Square tube 20 X 20 X 2_1 4 mitre 2
    split(bisect_by=Plane(origin=(-400, -250, 0), x_dir=(-0.707106781, -0.707106781, 0), z_dir=(-0.707106781, 0.707106781, 0)), keep=Keep.TOP)


with BuildPart() as body_5:
    # Sketch11 → Square tube 20 X 20 X 2(2) (new body)
    with BuildSketch(Plane.XZ.offset(-250)):
        with BuildLine():
            Line((-6, -10), (6, -10))
            ThreePointArc((6, -10), (8.828427125, -8.828427125), (10, -6))
            Line((10, -6), (10, 6))
            ThreePointArc((10, 6), (8.828427125, 8.828427125), (6, 10))
            Line((6, 10), (-6, 10))
            ThreePointArc((-6, 10), (-8.828427125, 8.828427125), (-10, 6))
            Line((-10, 6), (-10, -6))
            ThreePointArc((-10, -6), (-8.828427125, -8.828427125), (-6, -10))
        make_face()
        with BuildLine():
            Line((-6, -8), (6, -8))
            ThreePointArc((6, -8), (7.414213562, -7.414213562), (8, -6))
            Line((8, -6), (8, 6))
            ThreePointArc((8, 6), (7.414213562, 7.414213562), (6, 8))
            Line((6, 8), (-6, 8))
            ThreePointArc((-6, 8), (-7.414213562, 7.414213562), (-8, 6))
            Line((-8, 6), (-8, -6))
            ThreePointArc((-8, -6), (-7.414213562, -7.414213562), (-6, -8))
        make_face(mode=Mode.SUBTRACT)
    extrude(amount=SQUARE_TUBE_20_X_20_X_2_2_DEPTH)


solid = Compound([part.part, body_2.part, body_3.part, body_4.part, body_5.part])
